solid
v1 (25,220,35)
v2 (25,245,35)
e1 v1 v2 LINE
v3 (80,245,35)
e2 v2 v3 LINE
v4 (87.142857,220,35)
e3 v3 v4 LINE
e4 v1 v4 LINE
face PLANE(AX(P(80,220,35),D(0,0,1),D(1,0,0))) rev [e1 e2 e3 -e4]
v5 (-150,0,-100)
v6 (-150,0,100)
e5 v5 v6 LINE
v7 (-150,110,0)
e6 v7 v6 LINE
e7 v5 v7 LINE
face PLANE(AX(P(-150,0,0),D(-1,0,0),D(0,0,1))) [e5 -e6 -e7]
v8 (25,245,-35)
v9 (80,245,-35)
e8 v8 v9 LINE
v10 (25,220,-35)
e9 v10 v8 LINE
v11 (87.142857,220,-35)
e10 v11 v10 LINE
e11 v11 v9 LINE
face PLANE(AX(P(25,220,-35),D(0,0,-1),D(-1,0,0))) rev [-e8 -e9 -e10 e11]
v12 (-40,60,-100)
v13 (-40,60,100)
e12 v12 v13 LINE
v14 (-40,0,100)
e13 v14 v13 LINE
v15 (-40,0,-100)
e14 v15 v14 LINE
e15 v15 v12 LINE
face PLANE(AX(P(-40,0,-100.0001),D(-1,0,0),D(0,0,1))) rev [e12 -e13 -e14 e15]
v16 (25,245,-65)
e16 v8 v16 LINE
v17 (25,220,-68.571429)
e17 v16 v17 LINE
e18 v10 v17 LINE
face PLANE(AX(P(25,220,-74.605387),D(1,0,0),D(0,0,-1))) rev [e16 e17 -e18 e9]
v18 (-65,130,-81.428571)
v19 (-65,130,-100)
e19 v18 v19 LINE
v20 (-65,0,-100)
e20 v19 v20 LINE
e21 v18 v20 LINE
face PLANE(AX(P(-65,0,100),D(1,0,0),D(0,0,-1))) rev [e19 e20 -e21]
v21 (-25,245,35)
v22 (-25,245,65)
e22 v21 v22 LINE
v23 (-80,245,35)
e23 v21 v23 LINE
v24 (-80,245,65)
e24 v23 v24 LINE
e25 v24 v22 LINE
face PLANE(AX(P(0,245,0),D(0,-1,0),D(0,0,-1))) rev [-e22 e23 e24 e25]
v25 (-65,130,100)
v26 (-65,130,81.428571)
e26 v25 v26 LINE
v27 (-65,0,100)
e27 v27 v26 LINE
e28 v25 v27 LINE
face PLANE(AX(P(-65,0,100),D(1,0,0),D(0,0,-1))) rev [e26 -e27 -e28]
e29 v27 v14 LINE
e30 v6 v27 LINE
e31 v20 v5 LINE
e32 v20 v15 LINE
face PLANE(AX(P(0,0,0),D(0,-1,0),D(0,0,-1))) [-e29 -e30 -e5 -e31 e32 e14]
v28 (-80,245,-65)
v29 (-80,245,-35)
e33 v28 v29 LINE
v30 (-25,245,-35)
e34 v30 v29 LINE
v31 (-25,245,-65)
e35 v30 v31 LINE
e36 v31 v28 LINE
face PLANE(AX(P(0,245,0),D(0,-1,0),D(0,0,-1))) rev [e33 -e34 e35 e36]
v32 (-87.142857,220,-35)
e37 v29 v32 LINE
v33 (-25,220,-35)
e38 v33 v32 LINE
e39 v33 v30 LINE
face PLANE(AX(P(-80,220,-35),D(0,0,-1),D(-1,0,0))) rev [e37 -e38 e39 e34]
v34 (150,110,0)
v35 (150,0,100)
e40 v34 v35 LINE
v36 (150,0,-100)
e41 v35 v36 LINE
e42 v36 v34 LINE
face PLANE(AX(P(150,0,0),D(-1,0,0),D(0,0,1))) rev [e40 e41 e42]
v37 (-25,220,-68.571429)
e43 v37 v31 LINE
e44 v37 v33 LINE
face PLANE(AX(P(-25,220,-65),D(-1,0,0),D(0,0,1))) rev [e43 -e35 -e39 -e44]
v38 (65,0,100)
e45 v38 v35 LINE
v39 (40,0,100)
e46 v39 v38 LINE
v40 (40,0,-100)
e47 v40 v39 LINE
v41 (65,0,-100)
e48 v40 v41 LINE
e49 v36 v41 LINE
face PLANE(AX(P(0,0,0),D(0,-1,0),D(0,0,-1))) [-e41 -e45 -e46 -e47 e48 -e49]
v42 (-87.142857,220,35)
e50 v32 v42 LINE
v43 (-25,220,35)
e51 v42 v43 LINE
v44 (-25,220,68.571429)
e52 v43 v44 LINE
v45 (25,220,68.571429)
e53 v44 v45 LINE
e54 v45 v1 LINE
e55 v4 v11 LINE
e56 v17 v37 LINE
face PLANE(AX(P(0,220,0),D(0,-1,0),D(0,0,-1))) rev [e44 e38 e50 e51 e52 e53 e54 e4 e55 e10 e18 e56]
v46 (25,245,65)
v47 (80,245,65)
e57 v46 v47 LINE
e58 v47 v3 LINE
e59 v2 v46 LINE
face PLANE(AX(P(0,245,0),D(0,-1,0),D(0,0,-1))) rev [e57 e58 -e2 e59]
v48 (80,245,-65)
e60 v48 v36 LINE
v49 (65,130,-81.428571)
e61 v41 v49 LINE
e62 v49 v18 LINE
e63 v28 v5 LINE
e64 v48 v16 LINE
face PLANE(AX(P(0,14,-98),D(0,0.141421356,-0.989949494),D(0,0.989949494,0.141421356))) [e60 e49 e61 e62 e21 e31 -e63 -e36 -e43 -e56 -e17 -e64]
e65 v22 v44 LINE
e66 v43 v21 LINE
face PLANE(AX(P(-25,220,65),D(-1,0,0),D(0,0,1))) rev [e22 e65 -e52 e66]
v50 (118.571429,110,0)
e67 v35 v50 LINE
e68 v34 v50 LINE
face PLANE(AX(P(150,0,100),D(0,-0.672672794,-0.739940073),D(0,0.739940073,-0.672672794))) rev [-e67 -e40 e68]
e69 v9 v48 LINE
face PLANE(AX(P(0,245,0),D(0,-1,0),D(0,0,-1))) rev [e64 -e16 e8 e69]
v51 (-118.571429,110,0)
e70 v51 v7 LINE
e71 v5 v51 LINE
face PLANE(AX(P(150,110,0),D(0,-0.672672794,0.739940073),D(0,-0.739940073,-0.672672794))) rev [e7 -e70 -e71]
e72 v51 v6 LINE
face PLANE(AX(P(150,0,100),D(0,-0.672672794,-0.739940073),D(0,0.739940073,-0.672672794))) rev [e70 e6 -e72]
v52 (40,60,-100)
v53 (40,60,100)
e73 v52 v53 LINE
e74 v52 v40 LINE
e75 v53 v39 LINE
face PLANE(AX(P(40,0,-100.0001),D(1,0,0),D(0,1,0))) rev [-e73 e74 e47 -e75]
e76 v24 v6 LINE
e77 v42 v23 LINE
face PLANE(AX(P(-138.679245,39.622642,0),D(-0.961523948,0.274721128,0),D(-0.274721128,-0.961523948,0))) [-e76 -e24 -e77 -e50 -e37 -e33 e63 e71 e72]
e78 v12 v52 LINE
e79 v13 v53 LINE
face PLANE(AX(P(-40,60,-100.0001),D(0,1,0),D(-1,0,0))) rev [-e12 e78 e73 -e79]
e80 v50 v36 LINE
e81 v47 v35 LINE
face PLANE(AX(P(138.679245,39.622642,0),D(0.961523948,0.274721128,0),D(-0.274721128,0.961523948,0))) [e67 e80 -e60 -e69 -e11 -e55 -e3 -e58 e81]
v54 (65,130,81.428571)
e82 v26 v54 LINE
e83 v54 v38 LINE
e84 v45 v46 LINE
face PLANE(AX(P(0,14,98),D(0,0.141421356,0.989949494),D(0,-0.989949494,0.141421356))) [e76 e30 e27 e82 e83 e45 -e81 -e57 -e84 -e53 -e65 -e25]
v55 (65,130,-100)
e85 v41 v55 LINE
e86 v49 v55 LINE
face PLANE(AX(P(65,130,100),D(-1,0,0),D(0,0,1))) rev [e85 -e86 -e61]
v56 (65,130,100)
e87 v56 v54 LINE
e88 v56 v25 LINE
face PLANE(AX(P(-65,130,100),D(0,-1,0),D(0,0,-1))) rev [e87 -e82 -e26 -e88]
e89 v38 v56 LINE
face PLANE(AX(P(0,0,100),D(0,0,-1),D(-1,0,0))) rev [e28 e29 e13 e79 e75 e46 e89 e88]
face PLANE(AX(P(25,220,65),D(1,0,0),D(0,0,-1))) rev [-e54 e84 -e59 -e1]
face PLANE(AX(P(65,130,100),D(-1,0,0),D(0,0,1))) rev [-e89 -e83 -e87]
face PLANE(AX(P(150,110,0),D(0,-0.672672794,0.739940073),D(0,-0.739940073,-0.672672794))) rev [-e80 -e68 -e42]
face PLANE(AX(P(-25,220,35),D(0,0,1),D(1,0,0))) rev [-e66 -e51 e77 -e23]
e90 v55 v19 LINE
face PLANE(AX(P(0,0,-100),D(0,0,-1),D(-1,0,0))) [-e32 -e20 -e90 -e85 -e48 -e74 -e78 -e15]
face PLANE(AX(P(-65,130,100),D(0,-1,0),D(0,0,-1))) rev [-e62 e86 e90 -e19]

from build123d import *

# Parameters (mm, degrees)
GATE_BLOCK_PROFILE_130X130_W   = 130
GATE_BLOCK_PROFILE_130X130_H   = 130
GATE_BLOCK_DEPTH               = 100
SIDE_BUTTRESS_DEPTH            = 150
DOORWAY_CUT_DEPTH              = 305.179223648
DOORWAY_CUT_DEPTH_BACK         = 305.179223648
DOORWAY_PROFILE_60X80_W        = 80
DOORWAY_PROFILE_60X80_H        = 60
CRENELLATION_CUT_25_DEEP_DEPTH = 25


with BuildPart() as part:
    # Top Profile 160x130 → Pyramidal Body Loft section 0
    with BuildSketch(Plane(origin=(0, 245, 0), x_dir=(1, 0, 0), z_dir=(0, 1, 0))):
        with BuildLine():
            Line((-80, -65), (80, -65))
            Line((80, -65), (80, 65))
            Line((80, 65), (-80, 65))
            Line((-80, 65), (-80, -65))
        make_face()
    # Base Profile 300x200 → Pyramidal Body Loft section 1
    with BuildSketch(Plane(origin=(0, 0, 0), x_dir=(1, 0, 0), z_dir=(0, 1, 0))):
        with BuildLine():
            Line((-150, -100), (150, -100))
            Line((150, -100), (150, 100))
            Line((150, 100), (-150, 100))
            Line((-150, 100), (-150, -100))
        make_face()
    loft()

    # Gate Block Profile 130x130 → Gate Block (add, symmetric)
    with BuildSketch(Plane.XY):
        with Locations((0, 65)):
            Rectangle(GATE_BLOCK_PROFILE_130X130_W, GATE_BLOCK_PROFILE_130X130_H)
    extrude(amount=GATE_BLOCK_DEPTH, both=True)

    # Side Buttress Profile → Side Buttress (add, symmetric)
    with BuildSketch(Plane(origin=(0, 0, 0), x_dir=(0, 0, -1), z_dir=(1, 0, 0))):
        Polygon((-100, 0), (0, 110), (100, 0), align=None)
    extrude(amount=SIDE_BUTTRESS_DEPTH, both=True)

    # Doorway Profile 60x80 → Doorway Cut (cut, two sides: drawn at the far end of the back side and taken through both)
    with BuildSketch(Plane.XY.offset(-DOORWAY_CUT_DEPTH_BACK)):
        with Locations((0, 30)):
            Rectangle(DOORWAY_PROFILE_60X80_W, DOORWAY_PROFILE_60X80_H)
    extrude(amount=DOORWAY_CUT_DEPTH + DOORWAY_CUT_DEPTH_BACK, mode=Mode.SUBTRACT)

    # Crenellation Profile → Crenellation Cut 25 Deep (cut)
    with BuildSketch(Plane(origin=(0, 245, 0), x_dir=(1, 0, 0), z_dir=(0, 1, 0))):
        Polygon((-25, 65), (-25, 35), (-80, 35), (-93.798877222, 35), (-93.798877222, -35), (-80, -35), (-25, -35), (-25, -65), (-25, -87.972860003), (25, -87.972860003), (25, -65), (25, -35), (80, -35), (94.18727837, -35), (94.18727837, 35), (80, 35), (25, 35), (25, 65), (25, 74.605387162), (-25, 74.605387162), align=None)
    extrude(amount=-CRENELLATION_CUT_25_DEEP_DEPTH, mode=Mode.SUBTRACT)


solid = part.part
